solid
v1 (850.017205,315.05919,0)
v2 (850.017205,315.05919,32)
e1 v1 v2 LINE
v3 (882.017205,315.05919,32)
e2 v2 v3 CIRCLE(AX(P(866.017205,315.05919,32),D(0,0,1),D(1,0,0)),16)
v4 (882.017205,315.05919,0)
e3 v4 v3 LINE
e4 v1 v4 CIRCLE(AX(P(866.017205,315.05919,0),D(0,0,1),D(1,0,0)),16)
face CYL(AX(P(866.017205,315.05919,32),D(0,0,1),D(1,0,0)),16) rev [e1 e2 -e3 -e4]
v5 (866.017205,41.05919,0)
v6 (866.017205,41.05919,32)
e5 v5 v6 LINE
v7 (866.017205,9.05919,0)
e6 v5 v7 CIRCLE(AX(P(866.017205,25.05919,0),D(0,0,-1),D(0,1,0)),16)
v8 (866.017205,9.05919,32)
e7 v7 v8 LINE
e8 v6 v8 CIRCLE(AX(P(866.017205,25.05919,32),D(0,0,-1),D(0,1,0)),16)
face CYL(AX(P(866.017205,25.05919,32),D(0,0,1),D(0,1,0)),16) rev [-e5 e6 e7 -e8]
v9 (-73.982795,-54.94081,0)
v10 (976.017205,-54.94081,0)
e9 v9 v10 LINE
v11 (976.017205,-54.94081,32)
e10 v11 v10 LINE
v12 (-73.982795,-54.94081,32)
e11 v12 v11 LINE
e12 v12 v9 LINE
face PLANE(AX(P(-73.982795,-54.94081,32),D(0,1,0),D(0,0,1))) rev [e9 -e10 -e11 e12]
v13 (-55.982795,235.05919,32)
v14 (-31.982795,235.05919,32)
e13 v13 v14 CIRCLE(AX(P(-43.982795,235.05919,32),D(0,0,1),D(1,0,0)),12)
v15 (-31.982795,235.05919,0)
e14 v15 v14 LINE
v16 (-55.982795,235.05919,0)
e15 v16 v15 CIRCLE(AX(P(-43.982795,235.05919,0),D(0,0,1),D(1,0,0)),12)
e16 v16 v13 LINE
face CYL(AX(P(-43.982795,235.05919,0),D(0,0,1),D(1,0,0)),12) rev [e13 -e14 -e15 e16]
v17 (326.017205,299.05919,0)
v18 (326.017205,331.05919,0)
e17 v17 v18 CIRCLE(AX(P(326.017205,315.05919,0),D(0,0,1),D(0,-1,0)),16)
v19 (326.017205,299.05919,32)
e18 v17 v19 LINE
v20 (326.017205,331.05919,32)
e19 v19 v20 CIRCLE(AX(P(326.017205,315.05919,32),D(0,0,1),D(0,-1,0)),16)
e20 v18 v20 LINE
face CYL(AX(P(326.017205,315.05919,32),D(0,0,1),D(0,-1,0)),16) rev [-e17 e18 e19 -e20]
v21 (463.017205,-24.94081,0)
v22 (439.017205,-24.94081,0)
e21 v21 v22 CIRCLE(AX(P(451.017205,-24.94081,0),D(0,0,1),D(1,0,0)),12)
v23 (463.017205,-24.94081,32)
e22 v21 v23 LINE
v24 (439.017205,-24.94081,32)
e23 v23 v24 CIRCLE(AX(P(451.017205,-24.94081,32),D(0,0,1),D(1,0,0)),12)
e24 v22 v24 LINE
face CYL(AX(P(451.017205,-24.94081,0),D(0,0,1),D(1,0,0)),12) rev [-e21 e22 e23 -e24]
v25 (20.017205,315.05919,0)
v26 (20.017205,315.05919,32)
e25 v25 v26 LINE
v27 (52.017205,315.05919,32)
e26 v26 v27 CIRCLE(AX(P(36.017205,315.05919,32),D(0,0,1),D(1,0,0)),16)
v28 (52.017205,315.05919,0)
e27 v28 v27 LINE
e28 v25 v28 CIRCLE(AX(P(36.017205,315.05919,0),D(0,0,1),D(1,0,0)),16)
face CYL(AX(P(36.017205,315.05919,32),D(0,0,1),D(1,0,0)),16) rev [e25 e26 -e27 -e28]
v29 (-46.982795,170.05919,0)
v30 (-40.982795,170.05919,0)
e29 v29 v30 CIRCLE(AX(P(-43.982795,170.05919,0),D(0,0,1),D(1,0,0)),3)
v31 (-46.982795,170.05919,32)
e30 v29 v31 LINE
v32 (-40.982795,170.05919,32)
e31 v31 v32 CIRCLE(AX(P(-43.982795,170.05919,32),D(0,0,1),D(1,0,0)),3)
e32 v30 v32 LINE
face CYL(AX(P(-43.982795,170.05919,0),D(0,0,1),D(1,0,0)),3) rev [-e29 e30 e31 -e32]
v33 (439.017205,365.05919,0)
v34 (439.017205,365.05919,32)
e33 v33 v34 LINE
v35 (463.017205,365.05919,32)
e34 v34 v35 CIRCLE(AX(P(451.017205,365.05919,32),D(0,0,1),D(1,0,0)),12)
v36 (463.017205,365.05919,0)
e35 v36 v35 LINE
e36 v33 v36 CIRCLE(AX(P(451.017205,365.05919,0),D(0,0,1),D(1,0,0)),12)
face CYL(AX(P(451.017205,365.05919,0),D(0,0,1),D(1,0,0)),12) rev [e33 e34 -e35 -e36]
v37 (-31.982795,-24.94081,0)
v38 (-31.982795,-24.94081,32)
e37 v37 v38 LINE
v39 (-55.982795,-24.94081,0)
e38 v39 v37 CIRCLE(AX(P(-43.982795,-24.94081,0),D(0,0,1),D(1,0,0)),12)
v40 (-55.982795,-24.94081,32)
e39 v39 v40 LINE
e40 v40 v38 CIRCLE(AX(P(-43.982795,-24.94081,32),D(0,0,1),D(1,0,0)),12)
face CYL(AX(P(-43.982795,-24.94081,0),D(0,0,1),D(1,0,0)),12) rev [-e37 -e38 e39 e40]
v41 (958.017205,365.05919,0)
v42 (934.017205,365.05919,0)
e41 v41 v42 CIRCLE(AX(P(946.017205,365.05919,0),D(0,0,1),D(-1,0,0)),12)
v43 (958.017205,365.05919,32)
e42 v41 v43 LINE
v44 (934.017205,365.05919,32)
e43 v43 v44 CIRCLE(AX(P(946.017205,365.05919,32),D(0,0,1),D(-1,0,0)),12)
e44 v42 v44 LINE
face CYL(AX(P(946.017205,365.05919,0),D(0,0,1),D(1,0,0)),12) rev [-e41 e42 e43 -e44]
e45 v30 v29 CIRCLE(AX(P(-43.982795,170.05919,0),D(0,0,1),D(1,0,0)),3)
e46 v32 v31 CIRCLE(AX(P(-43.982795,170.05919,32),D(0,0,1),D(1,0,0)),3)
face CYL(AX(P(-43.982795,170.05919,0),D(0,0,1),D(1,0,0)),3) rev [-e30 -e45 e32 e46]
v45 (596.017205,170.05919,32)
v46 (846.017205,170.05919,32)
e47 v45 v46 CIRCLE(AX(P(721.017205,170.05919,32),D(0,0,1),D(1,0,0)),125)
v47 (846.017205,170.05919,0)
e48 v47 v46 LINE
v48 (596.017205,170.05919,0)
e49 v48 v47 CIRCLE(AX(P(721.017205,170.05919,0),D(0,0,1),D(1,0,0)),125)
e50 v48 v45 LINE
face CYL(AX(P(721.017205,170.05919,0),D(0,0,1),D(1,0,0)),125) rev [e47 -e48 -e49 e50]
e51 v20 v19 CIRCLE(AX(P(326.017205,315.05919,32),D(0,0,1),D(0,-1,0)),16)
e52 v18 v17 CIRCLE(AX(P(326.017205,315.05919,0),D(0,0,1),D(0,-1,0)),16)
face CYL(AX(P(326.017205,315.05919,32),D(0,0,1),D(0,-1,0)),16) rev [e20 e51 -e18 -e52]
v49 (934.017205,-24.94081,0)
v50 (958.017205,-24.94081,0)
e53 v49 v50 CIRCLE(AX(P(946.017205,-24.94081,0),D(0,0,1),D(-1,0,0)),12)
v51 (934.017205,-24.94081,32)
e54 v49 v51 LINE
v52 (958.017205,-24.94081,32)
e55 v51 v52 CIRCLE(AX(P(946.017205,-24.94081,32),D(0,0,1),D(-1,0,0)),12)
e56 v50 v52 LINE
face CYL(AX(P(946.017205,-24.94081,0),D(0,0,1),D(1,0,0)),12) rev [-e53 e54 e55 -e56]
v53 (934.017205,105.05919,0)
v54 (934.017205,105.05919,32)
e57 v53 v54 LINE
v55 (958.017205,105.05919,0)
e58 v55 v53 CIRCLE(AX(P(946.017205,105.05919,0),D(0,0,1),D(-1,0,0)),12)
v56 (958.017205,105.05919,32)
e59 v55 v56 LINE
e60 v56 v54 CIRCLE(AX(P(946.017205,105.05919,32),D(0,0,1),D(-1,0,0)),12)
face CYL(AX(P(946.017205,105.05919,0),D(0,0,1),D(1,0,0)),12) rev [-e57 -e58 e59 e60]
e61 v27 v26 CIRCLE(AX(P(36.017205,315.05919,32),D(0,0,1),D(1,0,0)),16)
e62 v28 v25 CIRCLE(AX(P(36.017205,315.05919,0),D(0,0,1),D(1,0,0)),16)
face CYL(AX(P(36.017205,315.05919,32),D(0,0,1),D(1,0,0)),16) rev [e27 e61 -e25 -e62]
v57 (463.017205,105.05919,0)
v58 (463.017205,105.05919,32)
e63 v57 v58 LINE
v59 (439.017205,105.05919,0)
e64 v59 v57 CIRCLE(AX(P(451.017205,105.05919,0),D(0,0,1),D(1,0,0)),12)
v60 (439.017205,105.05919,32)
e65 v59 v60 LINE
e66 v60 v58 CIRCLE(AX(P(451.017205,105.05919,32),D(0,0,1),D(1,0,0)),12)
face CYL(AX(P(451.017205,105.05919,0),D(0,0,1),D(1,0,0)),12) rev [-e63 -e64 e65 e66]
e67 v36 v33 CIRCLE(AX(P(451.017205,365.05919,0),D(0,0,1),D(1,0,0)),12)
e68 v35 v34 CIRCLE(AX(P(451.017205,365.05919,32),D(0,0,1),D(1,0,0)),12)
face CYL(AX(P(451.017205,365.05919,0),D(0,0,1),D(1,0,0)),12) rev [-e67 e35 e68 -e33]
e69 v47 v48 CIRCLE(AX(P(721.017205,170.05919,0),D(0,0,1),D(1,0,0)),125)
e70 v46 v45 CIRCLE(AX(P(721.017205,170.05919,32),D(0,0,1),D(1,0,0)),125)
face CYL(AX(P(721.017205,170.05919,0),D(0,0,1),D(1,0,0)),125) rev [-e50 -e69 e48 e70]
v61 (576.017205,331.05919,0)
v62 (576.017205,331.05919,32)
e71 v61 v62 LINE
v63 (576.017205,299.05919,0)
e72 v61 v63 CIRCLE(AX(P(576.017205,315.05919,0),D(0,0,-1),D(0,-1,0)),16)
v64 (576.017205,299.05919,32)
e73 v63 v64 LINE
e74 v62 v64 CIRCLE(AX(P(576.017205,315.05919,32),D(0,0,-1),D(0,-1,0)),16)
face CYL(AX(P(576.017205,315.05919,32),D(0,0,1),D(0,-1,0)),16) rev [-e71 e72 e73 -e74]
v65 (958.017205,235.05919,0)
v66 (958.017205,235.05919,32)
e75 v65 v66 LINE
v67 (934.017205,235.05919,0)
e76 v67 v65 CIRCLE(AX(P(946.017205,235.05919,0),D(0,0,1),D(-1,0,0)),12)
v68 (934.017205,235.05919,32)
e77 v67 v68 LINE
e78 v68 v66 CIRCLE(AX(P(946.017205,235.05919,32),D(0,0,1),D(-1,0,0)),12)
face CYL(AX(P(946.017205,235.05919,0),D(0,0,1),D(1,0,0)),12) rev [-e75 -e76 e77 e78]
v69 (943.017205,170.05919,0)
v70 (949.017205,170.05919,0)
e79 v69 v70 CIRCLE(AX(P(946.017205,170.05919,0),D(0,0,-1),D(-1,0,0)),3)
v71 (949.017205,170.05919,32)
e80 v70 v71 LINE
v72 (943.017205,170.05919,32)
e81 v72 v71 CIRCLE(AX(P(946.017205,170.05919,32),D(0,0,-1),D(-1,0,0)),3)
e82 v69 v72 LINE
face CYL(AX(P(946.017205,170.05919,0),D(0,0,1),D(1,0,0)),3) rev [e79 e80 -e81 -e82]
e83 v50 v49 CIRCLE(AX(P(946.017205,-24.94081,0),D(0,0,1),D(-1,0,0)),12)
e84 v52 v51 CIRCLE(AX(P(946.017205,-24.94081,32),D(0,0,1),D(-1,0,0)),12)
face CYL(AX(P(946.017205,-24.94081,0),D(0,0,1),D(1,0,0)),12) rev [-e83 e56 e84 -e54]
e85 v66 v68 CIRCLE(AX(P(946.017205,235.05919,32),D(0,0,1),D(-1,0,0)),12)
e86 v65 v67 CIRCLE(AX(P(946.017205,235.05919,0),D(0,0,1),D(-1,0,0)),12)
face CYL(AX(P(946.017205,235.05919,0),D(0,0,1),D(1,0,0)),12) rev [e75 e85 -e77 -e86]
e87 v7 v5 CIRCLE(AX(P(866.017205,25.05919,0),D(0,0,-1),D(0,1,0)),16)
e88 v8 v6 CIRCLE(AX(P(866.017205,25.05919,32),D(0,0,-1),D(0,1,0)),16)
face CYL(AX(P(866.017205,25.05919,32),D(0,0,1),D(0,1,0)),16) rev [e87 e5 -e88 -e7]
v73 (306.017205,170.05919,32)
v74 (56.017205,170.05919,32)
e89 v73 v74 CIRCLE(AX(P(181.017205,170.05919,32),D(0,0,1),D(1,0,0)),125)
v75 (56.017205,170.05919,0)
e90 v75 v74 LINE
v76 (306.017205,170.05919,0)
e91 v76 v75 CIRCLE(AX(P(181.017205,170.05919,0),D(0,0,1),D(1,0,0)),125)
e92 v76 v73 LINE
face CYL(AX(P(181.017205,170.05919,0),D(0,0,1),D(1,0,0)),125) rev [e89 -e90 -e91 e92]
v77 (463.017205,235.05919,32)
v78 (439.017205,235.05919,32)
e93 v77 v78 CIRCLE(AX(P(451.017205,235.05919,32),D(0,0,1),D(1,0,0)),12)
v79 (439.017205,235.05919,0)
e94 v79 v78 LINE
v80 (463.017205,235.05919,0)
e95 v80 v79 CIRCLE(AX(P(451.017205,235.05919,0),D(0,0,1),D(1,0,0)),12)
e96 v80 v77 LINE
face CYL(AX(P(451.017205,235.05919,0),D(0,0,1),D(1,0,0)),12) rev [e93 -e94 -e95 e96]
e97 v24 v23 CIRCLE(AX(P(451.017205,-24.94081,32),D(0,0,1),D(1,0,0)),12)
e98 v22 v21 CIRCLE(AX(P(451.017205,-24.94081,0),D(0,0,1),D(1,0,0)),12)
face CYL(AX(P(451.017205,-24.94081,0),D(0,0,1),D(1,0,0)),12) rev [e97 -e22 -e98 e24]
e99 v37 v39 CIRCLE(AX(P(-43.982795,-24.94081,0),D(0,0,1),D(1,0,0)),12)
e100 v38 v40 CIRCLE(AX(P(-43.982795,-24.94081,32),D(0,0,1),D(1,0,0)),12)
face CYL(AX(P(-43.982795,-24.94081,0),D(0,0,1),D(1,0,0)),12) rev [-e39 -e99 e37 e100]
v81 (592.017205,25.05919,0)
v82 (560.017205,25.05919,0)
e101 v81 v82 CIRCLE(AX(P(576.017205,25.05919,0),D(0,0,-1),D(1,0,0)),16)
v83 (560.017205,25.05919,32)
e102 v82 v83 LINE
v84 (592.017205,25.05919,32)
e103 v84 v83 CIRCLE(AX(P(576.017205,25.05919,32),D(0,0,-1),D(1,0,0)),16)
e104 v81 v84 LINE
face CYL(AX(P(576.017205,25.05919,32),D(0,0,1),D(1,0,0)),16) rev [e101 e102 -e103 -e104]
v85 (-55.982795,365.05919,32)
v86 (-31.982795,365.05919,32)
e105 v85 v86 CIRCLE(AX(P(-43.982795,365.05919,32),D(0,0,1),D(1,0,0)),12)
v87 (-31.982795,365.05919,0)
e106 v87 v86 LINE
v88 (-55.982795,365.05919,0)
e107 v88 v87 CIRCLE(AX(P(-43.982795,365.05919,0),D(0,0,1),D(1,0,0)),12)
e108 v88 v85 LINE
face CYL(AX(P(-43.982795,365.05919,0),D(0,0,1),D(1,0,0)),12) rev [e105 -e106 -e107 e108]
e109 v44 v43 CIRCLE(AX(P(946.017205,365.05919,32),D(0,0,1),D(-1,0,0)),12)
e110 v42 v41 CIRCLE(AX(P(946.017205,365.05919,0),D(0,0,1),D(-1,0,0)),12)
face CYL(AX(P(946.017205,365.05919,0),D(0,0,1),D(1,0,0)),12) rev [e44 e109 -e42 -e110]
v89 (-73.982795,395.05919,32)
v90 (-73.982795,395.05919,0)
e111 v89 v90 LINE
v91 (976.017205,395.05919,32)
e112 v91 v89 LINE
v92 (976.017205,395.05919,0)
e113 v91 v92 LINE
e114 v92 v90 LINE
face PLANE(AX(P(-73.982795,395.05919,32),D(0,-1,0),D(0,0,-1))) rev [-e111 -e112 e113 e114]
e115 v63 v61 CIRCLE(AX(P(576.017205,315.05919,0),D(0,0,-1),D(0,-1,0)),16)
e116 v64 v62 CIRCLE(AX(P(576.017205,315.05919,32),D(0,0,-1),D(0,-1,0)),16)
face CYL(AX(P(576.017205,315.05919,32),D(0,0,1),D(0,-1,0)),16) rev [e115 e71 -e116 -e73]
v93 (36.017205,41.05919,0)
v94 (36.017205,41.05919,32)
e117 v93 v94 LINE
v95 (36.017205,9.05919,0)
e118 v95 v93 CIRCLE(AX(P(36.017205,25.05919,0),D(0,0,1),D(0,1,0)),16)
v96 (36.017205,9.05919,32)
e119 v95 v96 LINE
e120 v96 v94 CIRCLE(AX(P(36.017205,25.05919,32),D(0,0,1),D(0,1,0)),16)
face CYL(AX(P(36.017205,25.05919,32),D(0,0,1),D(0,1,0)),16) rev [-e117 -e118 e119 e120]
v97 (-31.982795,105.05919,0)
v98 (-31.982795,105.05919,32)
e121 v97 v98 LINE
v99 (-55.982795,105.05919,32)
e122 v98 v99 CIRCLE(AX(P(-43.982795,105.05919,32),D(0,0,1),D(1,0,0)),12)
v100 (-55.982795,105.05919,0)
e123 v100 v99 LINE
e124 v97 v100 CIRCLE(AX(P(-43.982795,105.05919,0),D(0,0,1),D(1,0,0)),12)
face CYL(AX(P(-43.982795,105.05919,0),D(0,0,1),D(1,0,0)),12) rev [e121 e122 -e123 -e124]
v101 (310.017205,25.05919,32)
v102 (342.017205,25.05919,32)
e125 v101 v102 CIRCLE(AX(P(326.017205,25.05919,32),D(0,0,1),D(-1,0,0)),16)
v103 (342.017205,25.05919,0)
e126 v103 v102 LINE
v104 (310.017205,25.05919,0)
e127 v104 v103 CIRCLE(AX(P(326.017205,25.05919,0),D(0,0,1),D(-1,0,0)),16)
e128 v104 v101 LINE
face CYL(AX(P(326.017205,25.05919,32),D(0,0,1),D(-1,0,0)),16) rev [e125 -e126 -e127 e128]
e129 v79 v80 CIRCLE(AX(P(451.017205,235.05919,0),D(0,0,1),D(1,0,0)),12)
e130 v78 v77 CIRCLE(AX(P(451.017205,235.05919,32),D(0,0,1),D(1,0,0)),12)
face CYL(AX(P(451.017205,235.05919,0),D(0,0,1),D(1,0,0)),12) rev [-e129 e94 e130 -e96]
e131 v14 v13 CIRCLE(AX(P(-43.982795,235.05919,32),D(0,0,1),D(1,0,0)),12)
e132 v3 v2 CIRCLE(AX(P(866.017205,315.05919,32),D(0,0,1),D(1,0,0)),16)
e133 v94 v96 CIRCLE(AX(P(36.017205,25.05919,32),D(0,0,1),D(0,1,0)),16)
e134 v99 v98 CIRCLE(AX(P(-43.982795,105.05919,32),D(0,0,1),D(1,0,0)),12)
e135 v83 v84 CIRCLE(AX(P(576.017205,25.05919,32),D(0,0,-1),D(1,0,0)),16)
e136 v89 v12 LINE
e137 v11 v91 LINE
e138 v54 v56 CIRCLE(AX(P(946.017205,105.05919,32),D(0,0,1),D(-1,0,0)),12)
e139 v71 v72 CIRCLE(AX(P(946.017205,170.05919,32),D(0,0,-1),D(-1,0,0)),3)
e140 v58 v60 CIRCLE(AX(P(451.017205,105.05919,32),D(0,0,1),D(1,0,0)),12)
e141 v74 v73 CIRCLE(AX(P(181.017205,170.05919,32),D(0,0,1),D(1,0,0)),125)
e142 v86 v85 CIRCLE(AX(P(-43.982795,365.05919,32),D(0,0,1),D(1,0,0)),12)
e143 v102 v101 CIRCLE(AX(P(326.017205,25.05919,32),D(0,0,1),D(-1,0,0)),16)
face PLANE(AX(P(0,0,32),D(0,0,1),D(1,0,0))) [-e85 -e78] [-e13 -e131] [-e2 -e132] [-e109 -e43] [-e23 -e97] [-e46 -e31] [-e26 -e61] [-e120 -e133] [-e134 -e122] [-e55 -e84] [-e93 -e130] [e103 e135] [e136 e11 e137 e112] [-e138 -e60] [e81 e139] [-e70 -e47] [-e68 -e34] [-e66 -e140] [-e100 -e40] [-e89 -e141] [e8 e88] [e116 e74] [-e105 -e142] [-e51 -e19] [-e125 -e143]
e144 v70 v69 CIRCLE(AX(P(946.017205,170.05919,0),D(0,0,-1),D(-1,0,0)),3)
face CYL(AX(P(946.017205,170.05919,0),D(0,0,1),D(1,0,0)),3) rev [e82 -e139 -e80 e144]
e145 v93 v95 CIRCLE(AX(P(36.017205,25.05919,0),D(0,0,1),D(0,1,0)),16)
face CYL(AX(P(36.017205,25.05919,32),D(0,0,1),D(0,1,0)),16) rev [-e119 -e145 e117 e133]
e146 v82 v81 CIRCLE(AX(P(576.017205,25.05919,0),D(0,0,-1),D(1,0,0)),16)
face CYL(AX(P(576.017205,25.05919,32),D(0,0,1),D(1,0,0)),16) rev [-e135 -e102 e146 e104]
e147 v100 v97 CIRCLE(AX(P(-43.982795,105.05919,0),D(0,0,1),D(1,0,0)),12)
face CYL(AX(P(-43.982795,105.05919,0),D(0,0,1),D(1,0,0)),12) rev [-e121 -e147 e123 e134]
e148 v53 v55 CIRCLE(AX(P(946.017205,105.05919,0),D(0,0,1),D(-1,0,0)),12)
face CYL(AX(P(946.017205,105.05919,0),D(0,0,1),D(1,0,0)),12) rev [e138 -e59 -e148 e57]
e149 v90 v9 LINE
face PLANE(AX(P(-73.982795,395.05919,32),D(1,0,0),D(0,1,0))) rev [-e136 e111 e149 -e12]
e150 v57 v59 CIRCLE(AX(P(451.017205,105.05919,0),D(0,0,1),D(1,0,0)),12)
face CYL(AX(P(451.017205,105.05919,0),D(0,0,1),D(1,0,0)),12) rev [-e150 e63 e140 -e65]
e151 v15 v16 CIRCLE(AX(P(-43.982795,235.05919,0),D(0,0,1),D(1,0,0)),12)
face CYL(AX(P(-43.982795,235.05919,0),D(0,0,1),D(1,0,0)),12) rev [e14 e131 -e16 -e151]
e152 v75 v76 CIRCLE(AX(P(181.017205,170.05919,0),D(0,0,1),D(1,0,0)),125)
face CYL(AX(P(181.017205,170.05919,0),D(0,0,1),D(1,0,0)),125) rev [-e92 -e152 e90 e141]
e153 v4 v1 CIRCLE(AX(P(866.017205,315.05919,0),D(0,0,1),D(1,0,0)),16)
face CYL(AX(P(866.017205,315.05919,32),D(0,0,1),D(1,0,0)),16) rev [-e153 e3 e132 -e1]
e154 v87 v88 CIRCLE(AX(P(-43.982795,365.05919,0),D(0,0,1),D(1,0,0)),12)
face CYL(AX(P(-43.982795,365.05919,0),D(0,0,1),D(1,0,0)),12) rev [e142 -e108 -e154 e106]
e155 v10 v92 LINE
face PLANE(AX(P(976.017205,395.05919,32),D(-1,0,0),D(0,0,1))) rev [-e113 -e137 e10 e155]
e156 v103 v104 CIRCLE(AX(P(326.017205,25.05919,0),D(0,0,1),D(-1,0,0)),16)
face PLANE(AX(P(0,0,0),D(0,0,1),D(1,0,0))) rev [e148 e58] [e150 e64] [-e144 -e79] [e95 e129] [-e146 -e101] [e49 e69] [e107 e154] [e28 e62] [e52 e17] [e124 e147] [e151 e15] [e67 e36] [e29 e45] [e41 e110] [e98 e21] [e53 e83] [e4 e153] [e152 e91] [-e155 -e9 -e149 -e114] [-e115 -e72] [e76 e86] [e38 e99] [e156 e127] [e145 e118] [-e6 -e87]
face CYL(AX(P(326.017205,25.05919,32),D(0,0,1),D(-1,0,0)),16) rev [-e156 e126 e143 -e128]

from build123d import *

# Parameters (mm, degrees)
SKETCH1_W           = 1050
SKETCH1_H           = 450
BOSS_EXTRUDE1_DEPTH = 32
SKETCH2_R           = 125
CUT_EXTRUDE1_DEPTH  = 32
SKETCH3_R           = 12
CUT_EXTRUDE2_DEPTH  = 32
SKETCH7_R           = 3
CUT_EXTRUDE3_DEPTH  = 32
CIRPATTERN1_COUNT   = 4


with BuildPart() as part:
    # Sketch1 → Boss-Extrude1 (new body)
    with BuildSketch(Plane.XY):
        with Locations((451.017205348, 170.059190469)):
            Rectangle(SKETCH1_W, SKETCH1_H)
    extrude(amount=BOSS_EXTRUDE1_DEPTH)

    # Sketch2 → Cut-Extrude1 (cut)
    with BuildSketch(Plane.XY.offset(32)):
        with Locations((181.017205348, 170.059190469)):
            Circle(SKETCH2_R)
        with Locations((721.017205348, 170.059190469)):
            Circle(SKETCH2_R)
    extrude(amount=-CUT_EXTRUDE1_DEPTH, mode=Mode.SUBTRACT)

    # Sketch3 → Cut-Extrude2 (cut)
    with BuildSketch(Plane.XY.offset(32)):
        with Locations((-43.982794652, 365.059190469)):
            Circle(SKETCH3_R)
        with Locations((-43.982794652, 235.059190469)):
            Circle(SKETCH3_R)
        with Locations((-43.982794652, 105.059190469)):
            Circle(SKETCH3_R)
        with Locations((-43.982794652, -24.940809531)):
            Circle(SKETCH3_R)
        with Locations(Location((946.017205348, -24.940809531, 0), (0, 0, 180))):
            Circle(SKETCH3_R)
        with Locations(Location((946.017205348, 105.059190469, 0), (0, 0, 180))):
            Circle(SKETCH3_R)
        with Locations(Location((946.017205348, 235.059190469, 0), (0, 0, 180))):
            Circle(SKETCH3_R)
        with Locations(Location((946.017205348, 365.059190469, 0), (0, 0, 180))):
            Circle(SKETCH3_R)
        with Locations((451.017205348, 365.059190469)):
            Circle(SKETCH3_R)
        with Locations((451.017205348, 235.059190469)):
            Circle(SKETCH3_R)
        with Locations((451.017205348, 105.059190469)):
            Circle(SKETCH3_R)
        with Locations((451.017205348, -24.940809531)):
            Circle(SKETCH3_R)
    extrude(amount=-CUT_EXTRUDE2_DEPTH, mode=Mode.SUBTRACT)

    # Sketch5 → M36 Tapped Hole1 (revolve, cut)
    with BuildSketch(Plane(origin=(36.017205348, 315.059190469, 32), x_dir=(0, -1, 0), z_dir=(1, 0, 0))):
        Polygon((0, 0), (0, 101.613769904), (16, 92), (16, 0), align=None)
    m36_tapped_hole1 = revolve(axis=Axis((36.017205348, 315.059190469, 38.35), (0, 0, -1)), mode=Mode.SUBTRACT)

    # Mirror1: M36 Tapped Hole1 across plane
    add(m36_tapped_hole1.mirror(Plane.ZY.offset(-451.017205348)), mode=Mode.SUBTRACT)

    # Sketch7 → Cut-Extrude3 (cut)
    with BuildSketch(Plane.XY.offset(32)):
        with Locations((-43.982794652, 170.059190469)):
            Circle(SKETCH7_R)
    cut_extrude3 = extrude(amount=-CUT_EXTRUDE3_DEPTH, mode=Mode.SUBTRACT)

    # Mirror2: Cut-Extrude3 across plane
    add(cut_extrude3.mirror(Plane.ZY.offset(-451.017205348)), mode=Mode.SUBTRACT)

    # CirPattern1: M36 Tapped Hole1 ×4 about axis
    cirpattern1_axis = Axis((181.017205348, 170.059190469, 0), (0, 0, 1))
    for i in range(1, CIRPATTERN1_COUNT):
        add(m36_tapped_hole1.rotate(cirpattern1_axis, i * 360 / CIRPATTERN1_COUNT), mode=Mode.SUBTRACT)

    # Mirror3: M36 Tapped Hole1 across plane
    add(m36_tapped_hole1.mirror(Plane.ZY.offset(-451.017205348)), mode=Mode.SUBTRACT)

    # Mirror3 copy 1 sketch → Mirror3 copy 1 (revolve, cut)
    with BuildSketch(Plane(origin=(866.017205348, 25.059190469, 32), x_dir=(-1, 0, 0), z_dir=(0, 1, 0))):
        Polygon((0, 0), (0, -101.613769904), (16, -92), (16, 0), align=None)
    revolve(axis=Axis((866.017205348, 25.059190469, 38.35), (0, 0, 1)), mode=Mode.SUBTRACT)

    # Mirror3 copy 2 sketch → Mirror3 copy 2 (revolve, cut)
    with BuildSketch(Plane(origin=(576.017205348, 25.059190469, 32), x_dir=(0, 1, 0), z_dir=(1, 0, 0))):
        Polygon((0, 0), (0, -101.613769904), (16, -92), (16, 0), align=None)
    revolve(axis=Axis((576.017205348, 25.059190469, 38.35), (0, 0, 1)), mode=Mode.SUBTRACT)

    # Mirror3 copy 3 sketch → Mirror3 copy 3 (revolve, cut)
    with BuildSketch(Plane(origin=(576.017205348, 315.059190469, 32), x_dir=(1, 0, 0), z_dir=(0, -1, 0))):
        Polygon((0, 0), (0, -101.613769904), (16, -92), (16, 0), align=None)
    revolve(axis=Axis((576.017205348, 315.059190469, 38.35), (0, 0, 1)), mode=Mode.SUBTRACT)


solid = part.part
